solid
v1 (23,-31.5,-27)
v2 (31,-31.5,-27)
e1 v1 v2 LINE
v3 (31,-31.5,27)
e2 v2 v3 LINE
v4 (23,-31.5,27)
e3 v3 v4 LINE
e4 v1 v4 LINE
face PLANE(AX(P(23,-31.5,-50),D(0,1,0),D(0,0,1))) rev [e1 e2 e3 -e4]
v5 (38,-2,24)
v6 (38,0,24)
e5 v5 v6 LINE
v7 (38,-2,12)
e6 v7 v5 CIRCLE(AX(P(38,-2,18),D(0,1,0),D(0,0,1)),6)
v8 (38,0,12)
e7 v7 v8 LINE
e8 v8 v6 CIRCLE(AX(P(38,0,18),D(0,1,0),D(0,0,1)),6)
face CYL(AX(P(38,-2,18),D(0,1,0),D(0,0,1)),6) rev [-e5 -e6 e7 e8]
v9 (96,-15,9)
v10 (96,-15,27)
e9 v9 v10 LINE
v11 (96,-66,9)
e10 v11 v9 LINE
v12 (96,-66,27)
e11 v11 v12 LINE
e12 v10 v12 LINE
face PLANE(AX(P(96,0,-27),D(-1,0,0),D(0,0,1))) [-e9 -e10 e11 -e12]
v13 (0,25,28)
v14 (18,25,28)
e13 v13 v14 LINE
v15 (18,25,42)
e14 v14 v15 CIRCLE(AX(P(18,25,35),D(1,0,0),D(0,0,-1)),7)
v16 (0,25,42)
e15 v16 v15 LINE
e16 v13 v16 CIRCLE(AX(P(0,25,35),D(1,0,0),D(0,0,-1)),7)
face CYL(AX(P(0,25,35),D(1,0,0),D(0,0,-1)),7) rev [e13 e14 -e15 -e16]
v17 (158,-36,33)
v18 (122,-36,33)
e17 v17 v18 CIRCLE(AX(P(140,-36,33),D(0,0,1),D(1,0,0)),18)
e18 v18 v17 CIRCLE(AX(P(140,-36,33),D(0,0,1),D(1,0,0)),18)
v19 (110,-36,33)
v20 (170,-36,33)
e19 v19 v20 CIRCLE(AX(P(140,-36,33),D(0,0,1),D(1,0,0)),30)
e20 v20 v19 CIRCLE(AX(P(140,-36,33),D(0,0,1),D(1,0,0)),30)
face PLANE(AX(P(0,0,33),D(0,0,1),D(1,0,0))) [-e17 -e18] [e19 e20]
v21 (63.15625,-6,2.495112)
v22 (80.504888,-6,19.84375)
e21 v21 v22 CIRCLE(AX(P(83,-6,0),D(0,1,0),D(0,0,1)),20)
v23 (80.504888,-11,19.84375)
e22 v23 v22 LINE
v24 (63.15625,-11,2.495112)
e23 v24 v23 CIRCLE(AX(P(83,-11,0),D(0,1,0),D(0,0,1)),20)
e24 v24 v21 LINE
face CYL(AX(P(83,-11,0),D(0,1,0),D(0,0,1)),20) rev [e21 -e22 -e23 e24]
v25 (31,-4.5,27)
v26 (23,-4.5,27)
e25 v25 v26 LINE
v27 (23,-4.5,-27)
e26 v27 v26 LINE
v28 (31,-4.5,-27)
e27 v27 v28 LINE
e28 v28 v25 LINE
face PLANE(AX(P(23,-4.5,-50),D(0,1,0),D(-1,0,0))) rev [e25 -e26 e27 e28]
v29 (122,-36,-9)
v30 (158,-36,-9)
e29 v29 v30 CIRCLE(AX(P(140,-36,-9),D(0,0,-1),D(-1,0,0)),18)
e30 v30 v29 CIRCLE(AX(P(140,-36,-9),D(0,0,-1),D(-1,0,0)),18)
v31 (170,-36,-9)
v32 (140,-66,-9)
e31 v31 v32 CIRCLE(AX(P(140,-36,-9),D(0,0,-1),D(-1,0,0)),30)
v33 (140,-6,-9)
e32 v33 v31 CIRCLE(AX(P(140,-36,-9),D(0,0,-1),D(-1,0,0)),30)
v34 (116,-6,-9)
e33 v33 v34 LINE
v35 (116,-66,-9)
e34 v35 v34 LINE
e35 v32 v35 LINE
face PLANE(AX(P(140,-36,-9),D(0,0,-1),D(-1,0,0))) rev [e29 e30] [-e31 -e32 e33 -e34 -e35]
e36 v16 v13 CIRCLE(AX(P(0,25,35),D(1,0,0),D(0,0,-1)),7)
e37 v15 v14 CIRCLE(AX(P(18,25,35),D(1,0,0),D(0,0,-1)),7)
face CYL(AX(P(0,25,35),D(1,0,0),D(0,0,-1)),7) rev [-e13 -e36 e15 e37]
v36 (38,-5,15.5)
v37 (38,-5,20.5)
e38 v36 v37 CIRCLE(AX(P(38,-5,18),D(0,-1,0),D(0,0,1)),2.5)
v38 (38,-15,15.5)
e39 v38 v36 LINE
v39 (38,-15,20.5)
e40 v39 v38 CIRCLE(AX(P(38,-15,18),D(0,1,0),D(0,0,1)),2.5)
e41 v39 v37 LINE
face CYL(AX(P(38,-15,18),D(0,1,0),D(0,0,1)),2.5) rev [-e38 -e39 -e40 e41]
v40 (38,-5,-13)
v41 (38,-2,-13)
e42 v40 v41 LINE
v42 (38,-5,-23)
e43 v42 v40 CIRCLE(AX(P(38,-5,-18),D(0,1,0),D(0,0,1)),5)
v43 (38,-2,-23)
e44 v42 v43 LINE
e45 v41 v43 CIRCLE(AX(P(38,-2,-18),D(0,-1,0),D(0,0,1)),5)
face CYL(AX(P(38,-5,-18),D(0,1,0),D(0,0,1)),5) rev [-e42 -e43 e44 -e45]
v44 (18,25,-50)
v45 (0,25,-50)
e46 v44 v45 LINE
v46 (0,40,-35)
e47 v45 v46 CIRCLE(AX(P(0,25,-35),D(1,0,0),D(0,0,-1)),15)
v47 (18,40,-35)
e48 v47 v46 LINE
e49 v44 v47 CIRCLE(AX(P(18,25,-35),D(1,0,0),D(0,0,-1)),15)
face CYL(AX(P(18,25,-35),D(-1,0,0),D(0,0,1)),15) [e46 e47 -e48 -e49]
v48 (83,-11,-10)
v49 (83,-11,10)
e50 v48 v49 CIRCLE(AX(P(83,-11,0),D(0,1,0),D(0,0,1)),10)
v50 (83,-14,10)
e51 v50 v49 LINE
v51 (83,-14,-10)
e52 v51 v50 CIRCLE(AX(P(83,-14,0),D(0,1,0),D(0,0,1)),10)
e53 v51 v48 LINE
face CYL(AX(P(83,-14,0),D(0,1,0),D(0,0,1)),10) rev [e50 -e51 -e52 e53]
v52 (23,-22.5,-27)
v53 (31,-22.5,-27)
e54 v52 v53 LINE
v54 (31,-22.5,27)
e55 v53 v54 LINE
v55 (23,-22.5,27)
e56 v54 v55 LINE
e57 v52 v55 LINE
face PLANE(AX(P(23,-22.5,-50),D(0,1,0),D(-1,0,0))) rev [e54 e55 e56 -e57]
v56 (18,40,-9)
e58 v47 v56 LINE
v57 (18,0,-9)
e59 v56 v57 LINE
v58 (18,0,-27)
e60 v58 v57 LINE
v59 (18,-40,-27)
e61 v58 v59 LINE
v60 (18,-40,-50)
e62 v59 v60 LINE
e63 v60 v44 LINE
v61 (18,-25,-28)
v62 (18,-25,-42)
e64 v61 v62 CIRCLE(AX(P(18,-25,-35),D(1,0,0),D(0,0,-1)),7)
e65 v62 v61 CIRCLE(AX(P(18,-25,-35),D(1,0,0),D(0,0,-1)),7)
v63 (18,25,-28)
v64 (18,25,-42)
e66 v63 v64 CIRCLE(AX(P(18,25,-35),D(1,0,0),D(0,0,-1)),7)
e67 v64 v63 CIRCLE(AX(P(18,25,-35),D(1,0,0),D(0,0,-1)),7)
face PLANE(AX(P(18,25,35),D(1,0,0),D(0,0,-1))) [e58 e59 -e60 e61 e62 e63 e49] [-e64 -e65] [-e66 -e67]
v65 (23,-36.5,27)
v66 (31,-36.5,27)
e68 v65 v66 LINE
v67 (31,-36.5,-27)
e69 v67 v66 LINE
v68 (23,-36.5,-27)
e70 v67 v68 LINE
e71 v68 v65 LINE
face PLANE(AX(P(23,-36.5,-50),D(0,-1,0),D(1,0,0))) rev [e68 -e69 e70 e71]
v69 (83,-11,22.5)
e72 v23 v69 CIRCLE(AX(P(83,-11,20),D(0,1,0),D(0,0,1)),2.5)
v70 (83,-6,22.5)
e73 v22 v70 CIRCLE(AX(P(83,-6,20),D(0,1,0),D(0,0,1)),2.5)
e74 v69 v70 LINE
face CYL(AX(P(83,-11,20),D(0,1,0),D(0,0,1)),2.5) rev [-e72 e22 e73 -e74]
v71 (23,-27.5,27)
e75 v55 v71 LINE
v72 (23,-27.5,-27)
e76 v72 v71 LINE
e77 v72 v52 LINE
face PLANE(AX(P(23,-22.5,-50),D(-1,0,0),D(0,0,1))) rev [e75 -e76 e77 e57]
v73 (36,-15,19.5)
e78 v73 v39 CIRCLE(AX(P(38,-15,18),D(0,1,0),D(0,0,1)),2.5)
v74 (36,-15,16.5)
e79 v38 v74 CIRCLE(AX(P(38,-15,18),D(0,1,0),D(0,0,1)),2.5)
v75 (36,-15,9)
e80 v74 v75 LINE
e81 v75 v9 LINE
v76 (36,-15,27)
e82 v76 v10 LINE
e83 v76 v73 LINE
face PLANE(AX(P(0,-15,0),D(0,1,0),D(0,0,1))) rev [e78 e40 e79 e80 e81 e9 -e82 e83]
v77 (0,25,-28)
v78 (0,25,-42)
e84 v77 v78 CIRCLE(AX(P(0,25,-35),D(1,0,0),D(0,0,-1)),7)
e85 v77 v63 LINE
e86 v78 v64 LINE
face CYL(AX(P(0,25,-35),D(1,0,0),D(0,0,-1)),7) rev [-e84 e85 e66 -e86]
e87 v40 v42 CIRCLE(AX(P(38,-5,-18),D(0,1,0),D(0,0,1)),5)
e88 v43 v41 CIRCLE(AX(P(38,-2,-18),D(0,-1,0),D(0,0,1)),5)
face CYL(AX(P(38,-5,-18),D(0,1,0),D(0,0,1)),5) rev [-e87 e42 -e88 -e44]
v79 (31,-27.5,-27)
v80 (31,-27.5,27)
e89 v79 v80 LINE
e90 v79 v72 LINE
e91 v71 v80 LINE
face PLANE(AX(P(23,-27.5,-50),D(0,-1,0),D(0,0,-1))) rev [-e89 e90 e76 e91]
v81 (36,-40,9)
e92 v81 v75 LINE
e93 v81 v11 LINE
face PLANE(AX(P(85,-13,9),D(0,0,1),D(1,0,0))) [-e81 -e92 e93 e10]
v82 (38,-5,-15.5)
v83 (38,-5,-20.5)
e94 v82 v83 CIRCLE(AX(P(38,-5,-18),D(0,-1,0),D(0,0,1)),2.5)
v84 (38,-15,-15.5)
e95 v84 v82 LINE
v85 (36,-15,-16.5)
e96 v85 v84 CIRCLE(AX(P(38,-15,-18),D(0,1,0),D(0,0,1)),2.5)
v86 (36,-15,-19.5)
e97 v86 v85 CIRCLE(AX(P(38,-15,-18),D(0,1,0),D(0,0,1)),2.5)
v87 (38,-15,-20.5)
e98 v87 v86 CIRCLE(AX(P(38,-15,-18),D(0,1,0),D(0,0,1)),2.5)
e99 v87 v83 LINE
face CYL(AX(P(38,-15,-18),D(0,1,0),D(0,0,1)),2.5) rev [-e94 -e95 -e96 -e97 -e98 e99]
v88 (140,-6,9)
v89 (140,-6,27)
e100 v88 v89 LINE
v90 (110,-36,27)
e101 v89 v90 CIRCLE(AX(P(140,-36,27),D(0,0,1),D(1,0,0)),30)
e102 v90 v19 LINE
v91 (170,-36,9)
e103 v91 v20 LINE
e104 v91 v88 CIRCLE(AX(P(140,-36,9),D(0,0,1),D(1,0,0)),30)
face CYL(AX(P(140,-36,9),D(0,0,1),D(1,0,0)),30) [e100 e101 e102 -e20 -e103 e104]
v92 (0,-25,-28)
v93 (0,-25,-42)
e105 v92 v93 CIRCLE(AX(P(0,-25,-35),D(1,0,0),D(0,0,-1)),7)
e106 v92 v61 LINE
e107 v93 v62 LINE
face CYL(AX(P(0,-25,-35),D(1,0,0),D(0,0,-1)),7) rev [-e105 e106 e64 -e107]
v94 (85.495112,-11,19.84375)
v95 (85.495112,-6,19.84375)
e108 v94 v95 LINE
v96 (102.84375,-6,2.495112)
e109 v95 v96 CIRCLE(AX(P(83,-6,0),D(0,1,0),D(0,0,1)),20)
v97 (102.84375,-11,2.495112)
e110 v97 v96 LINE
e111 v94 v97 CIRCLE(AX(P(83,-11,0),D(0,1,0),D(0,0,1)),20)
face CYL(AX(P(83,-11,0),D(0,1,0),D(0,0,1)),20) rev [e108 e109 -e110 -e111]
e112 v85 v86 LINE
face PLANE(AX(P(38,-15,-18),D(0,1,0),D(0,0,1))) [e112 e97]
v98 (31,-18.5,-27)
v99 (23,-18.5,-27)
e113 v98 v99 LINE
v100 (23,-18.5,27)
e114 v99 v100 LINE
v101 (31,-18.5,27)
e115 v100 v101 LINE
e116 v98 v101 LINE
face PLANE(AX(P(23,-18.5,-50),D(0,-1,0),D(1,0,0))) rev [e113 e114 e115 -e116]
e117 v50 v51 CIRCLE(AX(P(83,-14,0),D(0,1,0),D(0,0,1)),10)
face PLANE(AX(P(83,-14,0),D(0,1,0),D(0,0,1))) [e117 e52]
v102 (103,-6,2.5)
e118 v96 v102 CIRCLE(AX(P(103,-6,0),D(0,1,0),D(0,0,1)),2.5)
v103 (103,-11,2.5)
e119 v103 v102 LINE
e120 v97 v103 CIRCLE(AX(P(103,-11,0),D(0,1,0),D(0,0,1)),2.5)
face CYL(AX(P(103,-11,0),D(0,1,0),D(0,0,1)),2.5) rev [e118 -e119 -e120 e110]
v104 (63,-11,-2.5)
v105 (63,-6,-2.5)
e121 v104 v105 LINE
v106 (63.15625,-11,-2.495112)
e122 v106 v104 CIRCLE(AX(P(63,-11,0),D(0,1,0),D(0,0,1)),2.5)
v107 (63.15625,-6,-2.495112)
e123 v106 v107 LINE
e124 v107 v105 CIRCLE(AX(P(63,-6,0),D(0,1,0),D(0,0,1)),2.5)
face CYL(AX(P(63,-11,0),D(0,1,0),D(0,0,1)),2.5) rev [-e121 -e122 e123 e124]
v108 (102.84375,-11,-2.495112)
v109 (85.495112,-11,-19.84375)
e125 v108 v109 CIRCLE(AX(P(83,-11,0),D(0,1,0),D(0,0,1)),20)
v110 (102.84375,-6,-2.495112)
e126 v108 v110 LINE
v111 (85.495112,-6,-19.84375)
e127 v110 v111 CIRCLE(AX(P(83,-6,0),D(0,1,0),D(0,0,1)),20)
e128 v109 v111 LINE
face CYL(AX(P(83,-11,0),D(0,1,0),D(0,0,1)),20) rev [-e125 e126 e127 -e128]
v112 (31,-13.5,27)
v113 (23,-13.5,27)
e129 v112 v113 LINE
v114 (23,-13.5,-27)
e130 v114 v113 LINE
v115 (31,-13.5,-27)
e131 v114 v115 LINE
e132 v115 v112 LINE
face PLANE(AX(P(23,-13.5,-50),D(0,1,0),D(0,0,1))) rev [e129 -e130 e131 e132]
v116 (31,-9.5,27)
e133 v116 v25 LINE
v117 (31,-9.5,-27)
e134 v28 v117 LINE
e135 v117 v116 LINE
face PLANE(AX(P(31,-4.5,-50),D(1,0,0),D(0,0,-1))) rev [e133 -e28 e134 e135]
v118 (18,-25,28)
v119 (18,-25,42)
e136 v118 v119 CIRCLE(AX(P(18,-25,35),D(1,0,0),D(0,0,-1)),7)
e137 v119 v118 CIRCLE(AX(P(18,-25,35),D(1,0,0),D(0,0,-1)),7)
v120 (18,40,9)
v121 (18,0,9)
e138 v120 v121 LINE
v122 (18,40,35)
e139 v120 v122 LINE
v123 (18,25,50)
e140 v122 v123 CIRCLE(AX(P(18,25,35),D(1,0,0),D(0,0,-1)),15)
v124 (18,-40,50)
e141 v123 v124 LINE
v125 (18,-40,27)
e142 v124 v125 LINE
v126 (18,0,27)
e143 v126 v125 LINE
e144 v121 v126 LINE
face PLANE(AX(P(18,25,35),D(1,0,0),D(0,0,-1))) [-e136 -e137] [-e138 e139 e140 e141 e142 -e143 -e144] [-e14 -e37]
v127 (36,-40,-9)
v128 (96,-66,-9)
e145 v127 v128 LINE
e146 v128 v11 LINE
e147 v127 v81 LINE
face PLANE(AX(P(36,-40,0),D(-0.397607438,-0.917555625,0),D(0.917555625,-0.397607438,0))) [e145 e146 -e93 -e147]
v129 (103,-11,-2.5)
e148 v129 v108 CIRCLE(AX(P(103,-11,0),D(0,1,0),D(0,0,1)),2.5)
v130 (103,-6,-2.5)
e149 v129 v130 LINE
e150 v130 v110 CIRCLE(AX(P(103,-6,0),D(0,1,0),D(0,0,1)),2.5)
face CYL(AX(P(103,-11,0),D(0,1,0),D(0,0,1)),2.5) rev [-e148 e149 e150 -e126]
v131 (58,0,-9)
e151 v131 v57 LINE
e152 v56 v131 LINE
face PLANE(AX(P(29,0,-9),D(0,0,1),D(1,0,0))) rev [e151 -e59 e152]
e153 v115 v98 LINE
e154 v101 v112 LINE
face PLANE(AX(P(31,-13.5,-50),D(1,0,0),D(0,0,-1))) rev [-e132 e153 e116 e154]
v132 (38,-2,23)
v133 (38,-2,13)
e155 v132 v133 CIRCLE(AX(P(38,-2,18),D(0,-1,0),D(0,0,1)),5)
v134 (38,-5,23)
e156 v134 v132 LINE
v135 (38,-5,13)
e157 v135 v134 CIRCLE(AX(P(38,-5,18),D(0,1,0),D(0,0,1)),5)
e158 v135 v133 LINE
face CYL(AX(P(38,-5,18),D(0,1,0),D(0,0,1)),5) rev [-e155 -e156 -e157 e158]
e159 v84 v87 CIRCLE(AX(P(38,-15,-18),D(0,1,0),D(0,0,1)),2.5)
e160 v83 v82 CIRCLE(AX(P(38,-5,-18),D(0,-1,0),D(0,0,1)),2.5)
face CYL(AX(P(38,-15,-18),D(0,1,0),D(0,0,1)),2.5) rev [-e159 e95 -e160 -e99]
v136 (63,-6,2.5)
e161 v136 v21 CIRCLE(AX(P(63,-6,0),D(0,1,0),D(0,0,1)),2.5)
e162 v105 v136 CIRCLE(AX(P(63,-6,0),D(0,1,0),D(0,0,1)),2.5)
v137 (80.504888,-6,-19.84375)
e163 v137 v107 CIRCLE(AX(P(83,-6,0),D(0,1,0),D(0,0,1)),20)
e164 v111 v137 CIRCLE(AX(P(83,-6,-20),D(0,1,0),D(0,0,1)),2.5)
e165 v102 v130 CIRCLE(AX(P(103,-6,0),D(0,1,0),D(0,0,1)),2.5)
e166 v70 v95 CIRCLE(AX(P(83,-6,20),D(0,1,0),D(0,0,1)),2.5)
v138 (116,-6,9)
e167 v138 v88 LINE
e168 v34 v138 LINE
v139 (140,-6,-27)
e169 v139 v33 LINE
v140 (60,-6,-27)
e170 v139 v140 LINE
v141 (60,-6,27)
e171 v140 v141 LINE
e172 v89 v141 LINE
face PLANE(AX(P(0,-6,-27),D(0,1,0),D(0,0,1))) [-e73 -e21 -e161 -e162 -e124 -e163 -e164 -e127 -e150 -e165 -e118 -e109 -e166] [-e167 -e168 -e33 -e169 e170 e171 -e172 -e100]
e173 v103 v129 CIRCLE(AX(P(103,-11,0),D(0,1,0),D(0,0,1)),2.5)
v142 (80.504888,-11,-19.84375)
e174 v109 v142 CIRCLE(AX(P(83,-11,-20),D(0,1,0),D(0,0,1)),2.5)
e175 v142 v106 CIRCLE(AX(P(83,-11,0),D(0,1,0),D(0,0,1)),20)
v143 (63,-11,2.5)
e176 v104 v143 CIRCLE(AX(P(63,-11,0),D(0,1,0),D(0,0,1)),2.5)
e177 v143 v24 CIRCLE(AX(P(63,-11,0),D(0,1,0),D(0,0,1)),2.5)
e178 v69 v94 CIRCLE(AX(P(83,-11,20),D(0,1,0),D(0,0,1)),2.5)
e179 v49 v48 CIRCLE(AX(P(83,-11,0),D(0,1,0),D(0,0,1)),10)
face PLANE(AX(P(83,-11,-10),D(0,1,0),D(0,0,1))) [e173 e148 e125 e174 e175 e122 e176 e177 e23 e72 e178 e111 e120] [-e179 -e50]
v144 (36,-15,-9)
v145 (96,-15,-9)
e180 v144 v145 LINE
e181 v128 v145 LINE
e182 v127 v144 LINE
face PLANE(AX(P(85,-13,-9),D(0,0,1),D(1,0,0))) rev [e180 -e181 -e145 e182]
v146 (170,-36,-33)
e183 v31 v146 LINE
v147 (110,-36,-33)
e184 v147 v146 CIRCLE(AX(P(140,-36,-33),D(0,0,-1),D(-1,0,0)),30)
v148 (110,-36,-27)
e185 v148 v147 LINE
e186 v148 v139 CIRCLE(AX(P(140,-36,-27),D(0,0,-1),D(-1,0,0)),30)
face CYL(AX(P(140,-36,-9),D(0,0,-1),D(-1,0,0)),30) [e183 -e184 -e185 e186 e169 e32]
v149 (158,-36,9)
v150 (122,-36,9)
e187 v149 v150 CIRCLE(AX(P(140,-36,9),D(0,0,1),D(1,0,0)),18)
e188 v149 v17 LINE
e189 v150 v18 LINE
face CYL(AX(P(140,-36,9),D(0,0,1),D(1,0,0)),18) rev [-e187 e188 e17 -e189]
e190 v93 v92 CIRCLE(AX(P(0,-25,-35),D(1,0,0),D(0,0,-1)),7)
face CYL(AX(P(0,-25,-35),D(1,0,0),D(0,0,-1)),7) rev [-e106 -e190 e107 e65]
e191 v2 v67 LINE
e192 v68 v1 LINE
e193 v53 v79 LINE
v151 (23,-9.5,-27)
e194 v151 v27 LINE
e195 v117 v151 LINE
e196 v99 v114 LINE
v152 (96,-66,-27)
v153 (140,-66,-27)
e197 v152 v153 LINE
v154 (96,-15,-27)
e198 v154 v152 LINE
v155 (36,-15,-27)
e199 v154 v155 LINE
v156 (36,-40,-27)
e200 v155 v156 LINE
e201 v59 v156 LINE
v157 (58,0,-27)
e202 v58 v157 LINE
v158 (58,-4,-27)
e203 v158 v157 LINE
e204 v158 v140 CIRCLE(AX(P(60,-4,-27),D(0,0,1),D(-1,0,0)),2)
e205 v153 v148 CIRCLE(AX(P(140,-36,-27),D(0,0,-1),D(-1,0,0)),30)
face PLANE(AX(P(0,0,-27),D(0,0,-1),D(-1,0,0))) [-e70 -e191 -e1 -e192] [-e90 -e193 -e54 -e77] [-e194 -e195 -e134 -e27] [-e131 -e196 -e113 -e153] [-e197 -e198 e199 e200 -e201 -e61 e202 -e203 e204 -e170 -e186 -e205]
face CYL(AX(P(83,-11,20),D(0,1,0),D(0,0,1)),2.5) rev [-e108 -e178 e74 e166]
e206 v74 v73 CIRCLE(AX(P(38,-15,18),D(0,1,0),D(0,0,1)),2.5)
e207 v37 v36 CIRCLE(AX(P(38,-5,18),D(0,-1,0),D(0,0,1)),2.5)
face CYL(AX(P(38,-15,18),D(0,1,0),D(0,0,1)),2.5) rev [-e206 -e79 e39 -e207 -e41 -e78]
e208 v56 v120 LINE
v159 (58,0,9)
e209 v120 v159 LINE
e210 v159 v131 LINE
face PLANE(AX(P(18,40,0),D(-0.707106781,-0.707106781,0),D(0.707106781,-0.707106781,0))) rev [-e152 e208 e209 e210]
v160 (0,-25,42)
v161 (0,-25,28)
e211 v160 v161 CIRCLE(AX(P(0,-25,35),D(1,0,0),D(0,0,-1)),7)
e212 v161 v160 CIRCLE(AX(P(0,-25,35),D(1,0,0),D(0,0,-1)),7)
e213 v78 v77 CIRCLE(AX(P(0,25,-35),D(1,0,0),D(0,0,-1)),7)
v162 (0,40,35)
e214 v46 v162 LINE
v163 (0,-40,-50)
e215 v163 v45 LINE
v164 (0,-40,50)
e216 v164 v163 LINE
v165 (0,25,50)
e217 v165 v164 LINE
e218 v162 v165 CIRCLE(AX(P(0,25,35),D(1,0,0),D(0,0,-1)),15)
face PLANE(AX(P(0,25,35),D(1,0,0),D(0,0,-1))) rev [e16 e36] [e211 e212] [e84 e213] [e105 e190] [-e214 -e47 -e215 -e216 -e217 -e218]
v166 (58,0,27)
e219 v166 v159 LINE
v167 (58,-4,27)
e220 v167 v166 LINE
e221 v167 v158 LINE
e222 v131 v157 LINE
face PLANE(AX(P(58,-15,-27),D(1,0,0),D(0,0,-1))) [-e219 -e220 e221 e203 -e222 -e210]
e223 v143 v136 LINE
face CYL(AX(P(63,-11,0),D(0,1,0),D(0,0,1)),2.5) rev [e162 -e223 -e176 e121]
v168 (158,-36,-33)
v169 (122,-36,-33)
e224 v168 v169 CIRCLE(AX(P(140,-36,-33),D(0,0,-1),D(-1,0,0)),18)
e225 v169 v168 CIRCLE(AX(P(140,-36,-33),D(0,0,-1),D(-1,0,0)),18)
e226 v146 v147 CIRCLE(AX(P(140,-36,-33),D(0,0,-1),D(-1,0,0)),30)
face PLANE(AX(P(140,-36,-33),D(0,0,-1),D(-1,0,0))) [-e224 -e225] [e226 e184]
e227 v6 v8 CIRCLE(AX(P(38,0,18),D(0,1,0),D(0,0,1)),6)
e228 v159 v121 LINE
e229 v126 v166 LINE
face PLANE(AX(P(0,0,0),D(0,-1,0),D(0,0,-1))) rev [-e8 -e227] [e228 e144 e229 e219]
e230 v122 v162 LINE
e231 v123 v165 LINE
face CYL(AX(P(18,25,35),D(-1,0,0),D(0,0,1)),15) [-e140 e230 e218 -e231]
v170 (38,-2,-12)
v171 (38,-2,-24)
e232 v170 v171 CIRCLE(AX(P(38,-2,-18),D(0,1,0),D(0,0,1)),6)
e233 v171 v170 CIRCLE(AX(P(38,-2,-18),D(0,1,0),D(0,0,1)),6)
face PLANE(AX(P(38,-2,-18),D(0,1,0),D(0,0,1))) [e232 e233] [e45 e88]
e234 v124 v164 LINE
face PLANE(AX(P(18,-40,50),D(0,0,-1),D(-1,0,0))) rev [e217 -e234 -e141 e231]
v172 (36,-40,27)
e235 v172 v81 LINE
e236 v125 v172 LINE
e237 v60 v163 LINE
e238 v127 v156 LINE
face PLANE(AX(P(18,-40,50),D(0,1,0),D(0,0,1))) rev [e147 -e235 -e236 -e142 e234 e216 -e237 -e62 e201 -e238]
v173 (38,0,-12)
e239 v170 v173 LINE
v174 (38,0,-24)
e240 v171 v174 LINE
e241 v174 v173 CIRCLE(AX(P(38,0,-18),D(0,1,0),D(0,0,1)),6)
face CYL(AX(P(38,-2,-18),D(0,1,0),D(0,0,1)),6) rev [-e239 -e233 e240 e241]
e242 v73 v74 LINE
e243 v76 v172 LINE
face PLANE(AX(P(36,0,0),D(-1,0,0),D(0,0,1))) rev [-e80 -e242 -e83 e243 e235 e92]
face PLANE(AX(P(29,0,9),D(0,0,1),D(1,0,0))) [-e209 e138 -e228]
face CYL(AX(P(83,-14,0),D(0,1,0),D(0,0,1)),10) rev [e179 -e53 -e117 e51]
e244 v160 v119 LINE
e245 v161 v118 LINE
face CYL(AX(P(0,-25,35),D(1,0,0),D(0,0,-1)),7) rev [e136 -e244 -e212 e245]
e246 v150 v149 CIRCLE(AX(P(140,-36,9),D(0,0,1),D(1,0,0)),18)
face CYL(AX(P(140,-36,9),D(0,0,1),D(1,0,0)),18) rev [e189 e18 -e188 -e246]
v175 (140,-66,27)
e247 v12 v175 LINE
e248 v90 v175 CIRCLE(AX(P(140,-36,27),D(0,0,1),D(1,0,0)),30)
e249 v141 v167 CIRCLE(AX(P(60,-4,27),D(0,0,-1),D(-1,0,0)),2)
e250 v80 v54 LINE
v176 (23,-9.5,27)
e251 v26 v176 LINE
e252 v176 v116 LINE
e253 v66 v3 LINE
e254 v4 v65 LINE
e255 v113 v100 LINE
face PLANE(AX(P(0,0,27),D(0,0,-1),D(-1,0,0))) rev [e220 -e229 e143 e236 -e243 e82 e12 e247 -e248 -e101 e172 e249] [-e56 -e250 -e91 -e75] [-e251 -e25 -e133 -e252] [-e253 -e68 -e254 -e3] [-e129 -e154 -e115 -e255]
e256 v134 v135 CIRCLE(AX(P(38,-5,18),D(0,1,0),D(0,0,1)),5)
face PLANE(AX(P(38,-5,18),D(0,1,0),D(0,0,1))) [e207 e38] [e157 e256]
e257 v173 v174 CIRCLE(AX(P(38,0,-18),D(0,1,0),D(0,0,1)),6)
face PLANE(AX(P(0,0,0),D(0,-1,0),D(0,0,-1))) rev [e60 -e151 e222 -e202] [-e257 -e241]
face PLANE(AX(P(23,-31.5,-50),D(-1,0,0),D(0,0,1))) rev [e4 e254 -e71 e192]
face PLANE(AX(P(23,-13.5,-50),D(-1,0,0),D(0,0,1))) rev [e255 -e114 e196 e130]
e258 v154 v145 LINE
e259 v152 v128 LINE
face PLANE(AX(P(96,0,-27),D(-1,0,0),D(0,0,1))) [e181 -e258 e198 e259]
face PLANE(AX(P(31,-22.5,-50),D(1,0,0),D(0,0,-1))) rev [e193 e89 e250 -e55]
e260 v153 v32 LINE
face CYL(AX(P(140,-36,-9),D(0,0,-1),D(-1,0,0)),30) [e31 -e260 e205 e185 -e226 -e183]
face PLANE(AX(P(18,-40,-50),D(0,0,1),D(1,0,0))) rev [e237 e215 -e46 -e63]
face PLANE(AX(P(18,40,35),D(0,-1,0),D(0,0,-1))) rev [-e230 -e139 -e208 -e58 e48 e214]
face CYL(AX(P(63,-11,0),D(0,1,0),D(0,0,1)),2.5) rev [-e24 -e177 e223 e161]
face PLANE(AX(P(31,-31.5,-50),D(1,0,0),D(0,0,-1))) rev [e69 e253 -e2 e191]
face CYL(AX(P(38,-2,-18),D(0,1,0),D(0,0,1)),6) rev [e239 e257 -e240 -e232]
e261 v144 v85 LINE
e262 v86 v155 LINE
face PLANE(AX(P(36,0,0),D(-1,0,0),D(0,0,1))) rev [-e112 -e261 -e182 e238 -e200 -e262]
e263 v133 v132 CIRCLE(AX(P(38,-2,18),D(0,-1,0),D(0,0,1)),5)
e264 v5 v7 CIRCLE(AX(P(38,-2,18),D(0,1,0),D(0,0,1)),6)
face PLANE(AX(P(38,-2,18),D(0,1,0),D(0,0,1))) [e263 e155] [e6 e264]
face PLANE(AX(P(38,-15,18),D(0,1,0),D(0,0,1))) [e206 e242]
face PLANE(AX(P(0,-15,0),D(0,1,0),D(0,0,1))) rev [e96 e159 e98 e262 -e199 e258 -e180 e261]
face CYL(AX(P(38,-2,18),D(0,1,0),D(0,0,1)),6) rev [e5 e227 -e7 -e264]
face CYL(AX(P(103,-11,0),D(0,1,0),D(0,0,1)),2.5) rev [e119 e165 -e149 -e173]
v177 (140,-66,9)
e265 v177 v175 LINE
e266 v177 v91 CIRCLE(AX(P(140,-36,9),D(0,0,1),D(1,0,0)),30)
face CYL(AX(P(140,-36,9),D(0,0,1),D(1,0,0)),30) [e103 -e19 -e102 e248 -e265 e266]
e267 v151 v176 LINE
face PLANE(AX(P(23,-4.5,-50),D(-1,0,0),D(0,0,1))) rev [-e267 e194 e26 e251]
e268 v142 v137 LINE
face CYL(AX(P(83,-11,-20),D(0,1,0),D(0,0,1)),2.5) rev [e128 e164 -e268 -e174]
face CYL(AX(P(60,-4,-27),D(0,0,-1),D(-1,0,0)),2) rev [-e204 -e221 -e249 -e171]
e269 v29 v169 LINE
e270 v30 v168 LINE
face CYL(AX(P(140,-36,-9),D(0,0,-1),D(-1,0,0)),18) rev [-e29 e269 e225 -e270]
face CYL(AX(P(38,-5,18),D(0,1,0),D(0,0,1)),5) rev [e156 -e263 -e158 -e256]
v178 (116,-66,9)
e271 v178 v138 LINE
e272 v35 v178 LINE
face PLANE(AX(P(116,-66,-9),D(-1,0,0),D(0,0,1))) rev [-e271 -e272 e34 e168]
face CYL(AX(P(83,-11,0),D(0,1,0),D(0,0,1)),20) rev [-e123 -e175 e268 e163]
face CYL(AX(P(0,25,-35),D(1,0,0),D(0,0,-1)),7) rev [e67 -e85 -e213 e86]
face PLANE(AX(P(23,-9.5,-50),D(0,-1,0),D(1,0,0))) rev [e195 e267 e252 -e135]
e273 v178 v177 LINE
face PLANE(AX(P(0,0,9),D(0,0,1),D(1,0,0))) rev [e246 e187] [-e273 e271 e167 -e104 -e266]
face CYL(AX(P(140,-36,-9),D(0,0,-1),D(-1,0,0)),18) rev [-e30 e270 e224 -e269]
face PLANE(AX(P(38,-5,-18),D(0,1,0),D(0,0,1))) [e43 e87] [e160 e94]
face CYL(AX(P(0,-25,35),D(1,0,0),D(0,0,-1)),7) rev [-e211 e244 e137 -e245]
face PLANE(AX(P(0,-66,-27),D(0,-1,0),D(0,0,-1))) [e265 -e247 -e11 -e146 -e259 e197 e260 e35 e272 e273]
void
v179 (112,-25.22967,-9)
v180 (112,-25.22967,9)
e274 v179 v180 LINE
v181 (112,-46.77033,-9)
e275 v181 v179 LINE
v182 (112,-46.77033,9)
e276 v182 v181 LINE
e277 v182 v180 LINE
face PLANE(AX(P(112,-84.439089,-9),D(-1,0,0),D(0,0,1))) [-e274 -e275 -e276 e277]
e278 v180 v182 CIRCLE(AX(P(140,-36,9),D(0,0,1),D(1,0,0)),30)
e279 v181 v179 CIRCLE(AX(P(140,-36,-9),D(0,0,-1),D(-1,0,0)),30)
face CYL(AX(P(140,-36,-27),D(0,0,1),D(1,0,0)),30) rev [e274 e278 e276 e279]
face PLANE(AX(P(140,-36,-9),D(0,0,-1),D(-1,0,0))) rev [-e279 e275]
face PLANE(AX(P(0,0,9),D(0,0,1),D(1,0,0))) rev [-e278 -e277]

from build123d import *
from build123d.topology import SkipClean

# Parameters (mm, degrees)
MOUNTING_PLATE_SKETCH_R      = 9
MOUNTING_PLATE_DEPTH         = 18
ARM_BLOCK_SKETCH_W           = 18
ARM_BLOCK_SKETCH_H           = 54
ARM_BLOCK_DEPTH              = 40
PLATE_START                  = -18
PLATE_CORNER_BOSSES_SKETCH_R = 7
PLATE_CORNER_BOSSES_DEPTH    = 18
ARM_EXTENSION_SKETCH_W       = 40
ARM_EXTENSION_SKETCH_H       = 54
ARM_EXTENSION_DEPTH          = 15
UPPER_SUPPORT_RIB_REACH      = 88.394
UPPER_RIB_SKETCH_WALL_W      = 231.357431026
UPPER_RIB_SKETCH_WALL_H      = 18
CLEVIS_ARM_DEPTH             = 54
SKETCH7_4_R                  = 30
SKETCH7_4_R_2                = 18
CLEVIS_FACE_1_DEPTH          = 6
SKETCH7_5_R                  = 30
SKETCH7_5_R_2                = 18
CLEVIS_LUG_1_DEPTH           = 18
CLEVIS_START                 = -36
SKETCH7_6_R                  = 30
SKETCH7_6_R_2                = 18
CLEVIS_LUG_2_DEPTH           = 18
CLEVIS_START_2               = -54
SKETCH7_7_R                  = 30
SKETCH7_7_R_2                = 18
CLEVIS_FACE_2_DEPTH          = 6
CLEVIS_PIN_BORE_SKETCH_W     = 24
CLEVIS_PIN_BORE_SKETCH_H     = 18
CLEVIS_PIN_BORE_24_DEPTH     = 188.082869339
LOWER_SUPPORT_RIB_REACH      = 191.093
LOWER_RIB_SKETCH_WALL_W      = 445.576270742
LOWER_RIB_SKETCH_WALL_H      = 18
CLEVIS_WEB_PAD_SKETCH_W      = 4
CLEVIS_WEB_PAD_SKETCH_H      = 18
CLEVIS_WEB_PAD_DEPTH         = 60
ARM_BLOCK_HOLES_SKETCH_R     = 2.5
ARM_BLOCK_HOLES_DEPTH        = 15
COUNTERBORE_10_SKETCH_R      = 5
COUNTERBORE_10_DEPTH         = 5
SPOTFACE_12_SKETCH_R         = 6
SPOTFACE_12_DEPTH            = 2
SIDE_SLOTS_4X_SKETCH_W       = 8
SIDE_SLOTS_4X_SKETCH_H       = 5
SIDE_SLOTS_4X_DEPTH          = 198.952014387
KEYED_RECESS_SKETCH_R        = 10
KEYED_RECESS_DEPTH           = 5
RECESS_BORE_20_SKETCH_R      = 10
RECESS_BORE_20_DEPTH         = 8
ARM_EDGE_FILLET_R2_R         = 2


with BuildPart() as part:
    # Mounting Plate Sketch → Mounting Plate (new body)
    with BuildSketch(Plane(origin=(0, 0, 0), x_dir=(0, 0, -1), z_dir=(1, 0, 0))):
        with BuildLine():
            Line((-50, -40), (50, -40))
            Line((50, -40), (50, 25))
            ThreePointArc((50, 25), (45.606601718, 35.606601718), (35, 40))
            Line((35, 40), (-35, 40))
            ThreePointArc((-35, 40), (-45.606601718, 35.606601718), (-50, 25))
            Line((-50, 25), (-50, -40))
        make_face()
        with Locations((-35, 25)):
            Circle(MOUNTING_PLATE_SKETCH_R, mode=Mode.SUBTRACT)
        with Locations((35, 25)):
            Circle(MOUNTING_PLATE_SKETCH_R, mode=Mode.SUBTRACT)
        with Locations((-35, -25)):
            Circle(MOUNTING_PLATE_SKETCH_R, mode=Mode.SUBTRACT)
        with Locations((35, -25)):
            Circle(MOUNTING_PLATE_SKETCH_R, mode=Mode.SUBTRACT)
    extrude(amount=MOUNTING_PLATE_DEPTH)

    # Arm Block Sketch → Arm Block (add)
    with BuildSketch(Plane.XZ.offset(40)):
        with Locations((27, 0)):
            Rectangle(ARM_BLOCK_SKETCH_W, ARM_BLOCK_SKETCH_H)
    extrude(amount=-ARM_BLOCK_DEPTH)

    # Plate Corner Bosses Sketch → Plate Corner Bosses (add)
    with BuildSketch(Plane(origin=(18, 0, 0), x_dir=(0, 0, -1), z_dir=(1, 0, 0)).offset(PLATE_START)):
        with BuildLine():
            Line((-35, 40), (35, 40))
            ThreePointArc((35, 40), (45.606601718, 35.606601718), (50, 25))
            Line((50, 25), (50, -40))
            Line((50, -40), (-50, -40))
            Line((-50, -40), (-50, 25))
            ThreePointArc((-50, 25), (-45.606601718, 35.606601718), (-35, 40))
        make_face()
        with Locations((-35, 25)):
            Circle(PLATE_CORNER_BOSSES_SKETCH_R, mode=Mode.SUBTRACT)
        with Locations((35, 25)):
            Circle(PLATE_CORNER_BOSSES_SKETCH_R, mode=Mode.SUBTRACT)
        with Locations((35, -25)):
            Circle(PLATE_CORNER_BOSSES_SKETCH_R, mode=Mode.SUBTRACT)
        with Locations((-35, -25)):
            Circle(PLATE_CORNER_BOSSES_SKETCH_R, mode=Mode.SUBTRACT)
    extrude(amount=PLATE_CORNER_BOSSES_DEPTH)

    # Arm Extension Sketch → Arm Extension (add)
    with BuildSketch(Plane(origin=(0, 0, 0), x_dir=(1, 0, 0), z_dir=(0, 1, 0))):
        with Locations((38, 0)):
            Rectangle(ARM_EXTENSION_SKETCH_W, ARM_EXTENSION_SKETCH_H)
    extrude(amount=-ARM_EXTENSION_DEPTH)

    # Upper Rib Sketch wall → Upper Support Rib (add, up to next)
    with BuildSketch(Plane(origin=(38, 20, 0), x_dir=(0.707106781187, -0.707106781187, 0), z_dir=(0.707106781187, 0.707106781187, 0)), mode=Mode.PRIVATE) as upper_support_rib_sk1:
        Rectangle(UPPER_RIB_SKETCH_WALL_W, UPPER_RIB_SKETCH_WALL_H)
    upper_support_rib_tool1 = extrude(upper_support_rib_sk1.sketch, amount=-UPPER_SUPPORT_RIB_REACH, mode=Mode.PRIVATE) - part.part
    add(upper_support_rib_tool1.solids().sort_by_distance((38, 20, 0))[0])

    # Clevis Arm Profile Sketch → Clevis Arm (add)
    with BuildSketch(Plane.XY.offset(27)):
        with BuildLine():
            ThreePointArc((140, -66), (110, -36), (140, -6))
            Line((140, -6), (58, -6))
            Line((58, -6), (58, -15))
            Line((58, -15), (96, -15))
            Line((96, -15), (96, -66))
            Line((96, -66), (140, -66))
        make_face()
    extrude(amount=-CLEVIS_ARM_DEPTH)



with BuildPart() as body_2:
    # Sketch7_4 → Clevis Face 1 (new body)
    with BuildSketch(Plane.XY.offset(27)):
        with Locations((140, -36)):
            Circle(SKETCH7_4_R)
        with Locations((140, -36)):
            Circle(SKETCH7_4_R_2, mode=Mode.SUBTRACT)
    extrude(amount=CLEVIS_FACE_1_DEPTH)


with BuildPart() as part_1:
    with SkipClean():  # the faces are left unmerged after this step: merging them gives an invalid solid
        add(part.part)

        add(body_2.part)  # Clevis Lug 1 merges body 2
        # Sketch7_5 → Clevis Lug 1 (add)
        with BuildSketch(Plane.XY.offset(27)):
            with Locations((140, -36)):
                Circle(SKETCH7_5_R)
            with Locations((140, -36)):
                Circle(SKETCH7_5_R_2, mode=Mode.SUBTRACT)
        extrude(amount=-CLEVIS_LUG_1_DEPTH)

    # Sketch7_6 → Clevis Lug 2 (add)
    with SkipClean():  # the faces are left unmerged after this step: merging them gives an invalid solid
        with BuildSketch(Plane.XY.offset(27).offset(CLEVIS_START)):
            with Locations((140, -36)):
                Circle(SKETCH7_6_R)
            with Locations((140, -36)):
                Circle(SKETCH7_6_R_2, mode=Mode.SUBTRACT)
        extrude(amount=-CLEVIS_LUG_2_DEPTH)

    # Sketch7_7 → Clevis Face 2 (add)
    with SkipClean():  # the faces are left unmerged after this step: merging them gives an invalid solid
        with BuildSketch(Plane.XY.offset(27).offset(CLEVIS_START_2)):
            with Locations((140, -36)):
                Circle(SKETCH7_7_R)
            with Locations((140, -36)):
                Circle(SKETCH7_7_R_2, mode=Mode.SUBTRACT)
        extrude(amount=-CLEVIS_FACE_2_DEPTH)

    # Clevis Pin Bore Sketch → Clevis Pin Bore _24 (cut, through all)
    with SkipClean():  # the faces are left unmerged after this step: merging them gives an invalid solid
        with BuildSketch(Plane(origin=(0, -6, 0), x_dir=(1, 0, 0), z_dir=(0, 1, 0))):
            with Locations((128, 0)):
                Rectangle(CLEVIS_PIN_BORE_SKETCH_W, CLEVIS_PIN_BORE_SKETCH_H)
        extrude(amount=-CLEVIS_PIN_BORE_24_DEPTH, mode=Mode.SUBTRACT)

    # Lower Rib Sketch wall → Lower Support Rib (add, up to next)
    with BuildSketch(Plane(origin=(66, -53, 0), x_dir=(0.91755562531, -0.397607437634, 0), z_dir=(0.397607437634, 0.91755562531, 0)), mode=Mode.PRIVATE) as lower_support_rib_sk1:
        Rectangle(LOWER_RIB_SKETCH_WALL_W, LOWER_RIB_SKETCH_WALL_H)
    lower_support_rib_tool1 = extrude(lower_support_rib_sk1.sketch, amount=LOWER_SUPPORT_RIB_REACH, mode=Mode.PRIVATE) - part_1.part
    add(lower_support_rib_tool1.solids().sort_by_distance((66, -53, 0))[0])

    # Clevis Web Pad Sketch → Clevis Web Pad (add)
    with SkipClean():  # the faces are left unmerged after this step: merging them gives an invalid solid
        with BuildSketch(Plane(origin=(0, -6, 0), x_dir=(1, 0, 0), z_dir=(0, 1, 0))):
            with Locations((114, 0)):
                Rectangle(CLEVIS_WEB_PAD_SKETCH_W, CLEVIS_WEB_PAD_SKETCH_H)
        extrude(amount=-CLEVIS_WEB_PAD_DEPTH)

    # Arm Block Holes Sketch → Arm Block Holes (cut)
    with SkipClean():  # the faces are left unmerged after this step: merging them gives an invalid solid
        with BuildSketch(Plane(origin=(0, 0, 0), x_dir=(1, 0, 0), z_dir=(0, 1, 0))):
            with Locations(Location((38, 18, 0), (0, 0, 270))):
                Circle(ARM_BLOCK_HOLES_SKETCH_R)
            with Locations(Location((38, -18, 0), (0, 0, 270))):
                Circle(ARM_BLOCK_HOLES_SKETCH_R)
        extrude(amount=-ARM_BLOCK_HOLES_DEPTH, mode=Mode.SUBTRACT)

    # Counterbore _10 Sketch → Counterbore _10 (cut)
    with SkipClean():  # the faces are left unmerged after this step: merging them gives an invalid solid
        with BuildSketch(Plane(origin=(0, 0, 0), x_dir=(1, 0, 0), z_dir=(0, 1, 0))):
            with Locations(Location((38, 18, 0), (0, 0, 270))):
                Circle(COUNTERBORE_10_SKETCH_R)
            with Locations(Location((38, -18, 0), (0, 0, 270))):
                Circle(COUNTERBORE_10_SKETCH_R)
        extrude(amount=-COUNTERBORE_10_DEPTH, mode=Mode.SUBTRACT)

    # Spotface _12 Sketch → Spotface _12 (cut)
    with SkipClean():  # the faces are left unmerged after this step: merging them gives an invalid solid
        with BuildSketch(Plane(origin=(0, 0, 0), x_dir=(1, 0, 0), z_dir=(0, 1, 0))):
            with Locations(Location((38, 18, 0), (0, 0, 270))):
                Circle(SPOTFACE_12_SKETCH_R)
            with Locations(Location((38, -18, 0), (0, 0, 270))):
                Circle(SPOTFACE_12_SKETCH_R)
        extrude(amount=-SPOTFACE_12_DEPTH, mode=Mode.SUBTRACT)

    # Side Slots 4x Sketch → Side Slots 4x (cut, through all)
    with SkipClean():  # the faces are left unmerged after this step: merging them gives an invalid solid
        with BuildSketch(Plane.XY.offset(27)):
            with Locations((27, -7)):
                Rectangle(SIDE_SLOTS_4X_SKETCH_W, SIDE_SLOTS_4X_SKETCH_H)
            with Locations((27, -16)):
                Rectangle(SIDE_SLOTS_4X_SKETCH_W, SIDE_SLOTS_4X_SKETCH_H)
            with Locations((27, -25)):
                Rectangle(SIDE_SLOTS_4X_SKETCH_W, SIDE_SLOTS_4X_SKETCH_H)
            with Locations((27, -34)):
                Rectangle(SIDE_SLOTS_4X_SKETCH_W, SIDE_SLOTS_4X_SKETCH_H)
        extrude(amount=-SIDE_SLOTS_4X_DEPTH, mode=Mode.SUBTRACT)

    # Keyed Recess Sketch → Keyed Recess (cut)
    with SkipClean():  # the faces are left unmerged after this step: merging them gives an invalid solid
        with BuildSketch(Plane(origin=(0, -6, 0), x_dir=(1, 0, 0), z_dir=(0, 1, 0))):
            with BuildLine():
                ThreePointArc((63.15625, -2.49511241), (68.857864376, -14.142135624), (80.50488759, -19.84375))
                ThreePointArc((80.50488759, -19.84375), (83, -22.5), (85.49511241, -19.84375))
                ThreePointArc((85.49511241, -19.84375), (97.142135624, -14.142135624), (102.84375, -2.49511241))
                ThreePointArc((102.84375, -2.49511241), (105.5, 0), (102.84375, 2.49511241))
                ThreePointArc((102.84375, 2.49511241), (97.142135624, 14.142135624), (85.49511241, 19.84375))
                ThreePointArc((85.49511241, 19.84375), (83, 22.5), (80.50488759, 19.84375))
                ThreePointArc((80.50488759, 19.84375), (68.857864376, 14.142135624), (63.15625, 2.49511241))
                ThreePointArc((63.15625, 2.49511241), (60.5, 0), (63.15625, -2.49511241))
            make_face()
            with Locations(Location((83, 0, 0), (0, 0, 270))):
                Circle(KEYED_RECESS_SKETCH_R, mode=Mode.SUBTRACT)
        extrude(amount=-KEYED_RECESS_DEPTH, mode=Mode.SUBTRACT)

    # Recess Bore _20 Sketch → Recess Bore _20 (cut)
    with SkipClean():  # the faces are left unmerged after this step: merging them gives an invalid solid
        with BuildSketch(Plane(origin=(0, -6, 0), x_dir=(1, 0, 0), z_dir=(0, 1, 0))):
            with Locations(Location((83, 0, 0), (0, 0, 270))):
                Circle(RECESS_BORE_20_SKETCH_R)
        extrude(amount=-RECESS_BORE_20_DEPTH, mode=Mode.SUBTRACT)

    # Arm Edge Fillet R2
    arm_edge_fillet_r2_edges = [part_1.edges().sort_by_distance(p)[0] for p in [
        (58, -6, 0),
    ]]
    fillet(arm_edge_fillet_r2_edges, radius=ARM_EDGE_FILLET_R2_R)


solid = part_1.part
